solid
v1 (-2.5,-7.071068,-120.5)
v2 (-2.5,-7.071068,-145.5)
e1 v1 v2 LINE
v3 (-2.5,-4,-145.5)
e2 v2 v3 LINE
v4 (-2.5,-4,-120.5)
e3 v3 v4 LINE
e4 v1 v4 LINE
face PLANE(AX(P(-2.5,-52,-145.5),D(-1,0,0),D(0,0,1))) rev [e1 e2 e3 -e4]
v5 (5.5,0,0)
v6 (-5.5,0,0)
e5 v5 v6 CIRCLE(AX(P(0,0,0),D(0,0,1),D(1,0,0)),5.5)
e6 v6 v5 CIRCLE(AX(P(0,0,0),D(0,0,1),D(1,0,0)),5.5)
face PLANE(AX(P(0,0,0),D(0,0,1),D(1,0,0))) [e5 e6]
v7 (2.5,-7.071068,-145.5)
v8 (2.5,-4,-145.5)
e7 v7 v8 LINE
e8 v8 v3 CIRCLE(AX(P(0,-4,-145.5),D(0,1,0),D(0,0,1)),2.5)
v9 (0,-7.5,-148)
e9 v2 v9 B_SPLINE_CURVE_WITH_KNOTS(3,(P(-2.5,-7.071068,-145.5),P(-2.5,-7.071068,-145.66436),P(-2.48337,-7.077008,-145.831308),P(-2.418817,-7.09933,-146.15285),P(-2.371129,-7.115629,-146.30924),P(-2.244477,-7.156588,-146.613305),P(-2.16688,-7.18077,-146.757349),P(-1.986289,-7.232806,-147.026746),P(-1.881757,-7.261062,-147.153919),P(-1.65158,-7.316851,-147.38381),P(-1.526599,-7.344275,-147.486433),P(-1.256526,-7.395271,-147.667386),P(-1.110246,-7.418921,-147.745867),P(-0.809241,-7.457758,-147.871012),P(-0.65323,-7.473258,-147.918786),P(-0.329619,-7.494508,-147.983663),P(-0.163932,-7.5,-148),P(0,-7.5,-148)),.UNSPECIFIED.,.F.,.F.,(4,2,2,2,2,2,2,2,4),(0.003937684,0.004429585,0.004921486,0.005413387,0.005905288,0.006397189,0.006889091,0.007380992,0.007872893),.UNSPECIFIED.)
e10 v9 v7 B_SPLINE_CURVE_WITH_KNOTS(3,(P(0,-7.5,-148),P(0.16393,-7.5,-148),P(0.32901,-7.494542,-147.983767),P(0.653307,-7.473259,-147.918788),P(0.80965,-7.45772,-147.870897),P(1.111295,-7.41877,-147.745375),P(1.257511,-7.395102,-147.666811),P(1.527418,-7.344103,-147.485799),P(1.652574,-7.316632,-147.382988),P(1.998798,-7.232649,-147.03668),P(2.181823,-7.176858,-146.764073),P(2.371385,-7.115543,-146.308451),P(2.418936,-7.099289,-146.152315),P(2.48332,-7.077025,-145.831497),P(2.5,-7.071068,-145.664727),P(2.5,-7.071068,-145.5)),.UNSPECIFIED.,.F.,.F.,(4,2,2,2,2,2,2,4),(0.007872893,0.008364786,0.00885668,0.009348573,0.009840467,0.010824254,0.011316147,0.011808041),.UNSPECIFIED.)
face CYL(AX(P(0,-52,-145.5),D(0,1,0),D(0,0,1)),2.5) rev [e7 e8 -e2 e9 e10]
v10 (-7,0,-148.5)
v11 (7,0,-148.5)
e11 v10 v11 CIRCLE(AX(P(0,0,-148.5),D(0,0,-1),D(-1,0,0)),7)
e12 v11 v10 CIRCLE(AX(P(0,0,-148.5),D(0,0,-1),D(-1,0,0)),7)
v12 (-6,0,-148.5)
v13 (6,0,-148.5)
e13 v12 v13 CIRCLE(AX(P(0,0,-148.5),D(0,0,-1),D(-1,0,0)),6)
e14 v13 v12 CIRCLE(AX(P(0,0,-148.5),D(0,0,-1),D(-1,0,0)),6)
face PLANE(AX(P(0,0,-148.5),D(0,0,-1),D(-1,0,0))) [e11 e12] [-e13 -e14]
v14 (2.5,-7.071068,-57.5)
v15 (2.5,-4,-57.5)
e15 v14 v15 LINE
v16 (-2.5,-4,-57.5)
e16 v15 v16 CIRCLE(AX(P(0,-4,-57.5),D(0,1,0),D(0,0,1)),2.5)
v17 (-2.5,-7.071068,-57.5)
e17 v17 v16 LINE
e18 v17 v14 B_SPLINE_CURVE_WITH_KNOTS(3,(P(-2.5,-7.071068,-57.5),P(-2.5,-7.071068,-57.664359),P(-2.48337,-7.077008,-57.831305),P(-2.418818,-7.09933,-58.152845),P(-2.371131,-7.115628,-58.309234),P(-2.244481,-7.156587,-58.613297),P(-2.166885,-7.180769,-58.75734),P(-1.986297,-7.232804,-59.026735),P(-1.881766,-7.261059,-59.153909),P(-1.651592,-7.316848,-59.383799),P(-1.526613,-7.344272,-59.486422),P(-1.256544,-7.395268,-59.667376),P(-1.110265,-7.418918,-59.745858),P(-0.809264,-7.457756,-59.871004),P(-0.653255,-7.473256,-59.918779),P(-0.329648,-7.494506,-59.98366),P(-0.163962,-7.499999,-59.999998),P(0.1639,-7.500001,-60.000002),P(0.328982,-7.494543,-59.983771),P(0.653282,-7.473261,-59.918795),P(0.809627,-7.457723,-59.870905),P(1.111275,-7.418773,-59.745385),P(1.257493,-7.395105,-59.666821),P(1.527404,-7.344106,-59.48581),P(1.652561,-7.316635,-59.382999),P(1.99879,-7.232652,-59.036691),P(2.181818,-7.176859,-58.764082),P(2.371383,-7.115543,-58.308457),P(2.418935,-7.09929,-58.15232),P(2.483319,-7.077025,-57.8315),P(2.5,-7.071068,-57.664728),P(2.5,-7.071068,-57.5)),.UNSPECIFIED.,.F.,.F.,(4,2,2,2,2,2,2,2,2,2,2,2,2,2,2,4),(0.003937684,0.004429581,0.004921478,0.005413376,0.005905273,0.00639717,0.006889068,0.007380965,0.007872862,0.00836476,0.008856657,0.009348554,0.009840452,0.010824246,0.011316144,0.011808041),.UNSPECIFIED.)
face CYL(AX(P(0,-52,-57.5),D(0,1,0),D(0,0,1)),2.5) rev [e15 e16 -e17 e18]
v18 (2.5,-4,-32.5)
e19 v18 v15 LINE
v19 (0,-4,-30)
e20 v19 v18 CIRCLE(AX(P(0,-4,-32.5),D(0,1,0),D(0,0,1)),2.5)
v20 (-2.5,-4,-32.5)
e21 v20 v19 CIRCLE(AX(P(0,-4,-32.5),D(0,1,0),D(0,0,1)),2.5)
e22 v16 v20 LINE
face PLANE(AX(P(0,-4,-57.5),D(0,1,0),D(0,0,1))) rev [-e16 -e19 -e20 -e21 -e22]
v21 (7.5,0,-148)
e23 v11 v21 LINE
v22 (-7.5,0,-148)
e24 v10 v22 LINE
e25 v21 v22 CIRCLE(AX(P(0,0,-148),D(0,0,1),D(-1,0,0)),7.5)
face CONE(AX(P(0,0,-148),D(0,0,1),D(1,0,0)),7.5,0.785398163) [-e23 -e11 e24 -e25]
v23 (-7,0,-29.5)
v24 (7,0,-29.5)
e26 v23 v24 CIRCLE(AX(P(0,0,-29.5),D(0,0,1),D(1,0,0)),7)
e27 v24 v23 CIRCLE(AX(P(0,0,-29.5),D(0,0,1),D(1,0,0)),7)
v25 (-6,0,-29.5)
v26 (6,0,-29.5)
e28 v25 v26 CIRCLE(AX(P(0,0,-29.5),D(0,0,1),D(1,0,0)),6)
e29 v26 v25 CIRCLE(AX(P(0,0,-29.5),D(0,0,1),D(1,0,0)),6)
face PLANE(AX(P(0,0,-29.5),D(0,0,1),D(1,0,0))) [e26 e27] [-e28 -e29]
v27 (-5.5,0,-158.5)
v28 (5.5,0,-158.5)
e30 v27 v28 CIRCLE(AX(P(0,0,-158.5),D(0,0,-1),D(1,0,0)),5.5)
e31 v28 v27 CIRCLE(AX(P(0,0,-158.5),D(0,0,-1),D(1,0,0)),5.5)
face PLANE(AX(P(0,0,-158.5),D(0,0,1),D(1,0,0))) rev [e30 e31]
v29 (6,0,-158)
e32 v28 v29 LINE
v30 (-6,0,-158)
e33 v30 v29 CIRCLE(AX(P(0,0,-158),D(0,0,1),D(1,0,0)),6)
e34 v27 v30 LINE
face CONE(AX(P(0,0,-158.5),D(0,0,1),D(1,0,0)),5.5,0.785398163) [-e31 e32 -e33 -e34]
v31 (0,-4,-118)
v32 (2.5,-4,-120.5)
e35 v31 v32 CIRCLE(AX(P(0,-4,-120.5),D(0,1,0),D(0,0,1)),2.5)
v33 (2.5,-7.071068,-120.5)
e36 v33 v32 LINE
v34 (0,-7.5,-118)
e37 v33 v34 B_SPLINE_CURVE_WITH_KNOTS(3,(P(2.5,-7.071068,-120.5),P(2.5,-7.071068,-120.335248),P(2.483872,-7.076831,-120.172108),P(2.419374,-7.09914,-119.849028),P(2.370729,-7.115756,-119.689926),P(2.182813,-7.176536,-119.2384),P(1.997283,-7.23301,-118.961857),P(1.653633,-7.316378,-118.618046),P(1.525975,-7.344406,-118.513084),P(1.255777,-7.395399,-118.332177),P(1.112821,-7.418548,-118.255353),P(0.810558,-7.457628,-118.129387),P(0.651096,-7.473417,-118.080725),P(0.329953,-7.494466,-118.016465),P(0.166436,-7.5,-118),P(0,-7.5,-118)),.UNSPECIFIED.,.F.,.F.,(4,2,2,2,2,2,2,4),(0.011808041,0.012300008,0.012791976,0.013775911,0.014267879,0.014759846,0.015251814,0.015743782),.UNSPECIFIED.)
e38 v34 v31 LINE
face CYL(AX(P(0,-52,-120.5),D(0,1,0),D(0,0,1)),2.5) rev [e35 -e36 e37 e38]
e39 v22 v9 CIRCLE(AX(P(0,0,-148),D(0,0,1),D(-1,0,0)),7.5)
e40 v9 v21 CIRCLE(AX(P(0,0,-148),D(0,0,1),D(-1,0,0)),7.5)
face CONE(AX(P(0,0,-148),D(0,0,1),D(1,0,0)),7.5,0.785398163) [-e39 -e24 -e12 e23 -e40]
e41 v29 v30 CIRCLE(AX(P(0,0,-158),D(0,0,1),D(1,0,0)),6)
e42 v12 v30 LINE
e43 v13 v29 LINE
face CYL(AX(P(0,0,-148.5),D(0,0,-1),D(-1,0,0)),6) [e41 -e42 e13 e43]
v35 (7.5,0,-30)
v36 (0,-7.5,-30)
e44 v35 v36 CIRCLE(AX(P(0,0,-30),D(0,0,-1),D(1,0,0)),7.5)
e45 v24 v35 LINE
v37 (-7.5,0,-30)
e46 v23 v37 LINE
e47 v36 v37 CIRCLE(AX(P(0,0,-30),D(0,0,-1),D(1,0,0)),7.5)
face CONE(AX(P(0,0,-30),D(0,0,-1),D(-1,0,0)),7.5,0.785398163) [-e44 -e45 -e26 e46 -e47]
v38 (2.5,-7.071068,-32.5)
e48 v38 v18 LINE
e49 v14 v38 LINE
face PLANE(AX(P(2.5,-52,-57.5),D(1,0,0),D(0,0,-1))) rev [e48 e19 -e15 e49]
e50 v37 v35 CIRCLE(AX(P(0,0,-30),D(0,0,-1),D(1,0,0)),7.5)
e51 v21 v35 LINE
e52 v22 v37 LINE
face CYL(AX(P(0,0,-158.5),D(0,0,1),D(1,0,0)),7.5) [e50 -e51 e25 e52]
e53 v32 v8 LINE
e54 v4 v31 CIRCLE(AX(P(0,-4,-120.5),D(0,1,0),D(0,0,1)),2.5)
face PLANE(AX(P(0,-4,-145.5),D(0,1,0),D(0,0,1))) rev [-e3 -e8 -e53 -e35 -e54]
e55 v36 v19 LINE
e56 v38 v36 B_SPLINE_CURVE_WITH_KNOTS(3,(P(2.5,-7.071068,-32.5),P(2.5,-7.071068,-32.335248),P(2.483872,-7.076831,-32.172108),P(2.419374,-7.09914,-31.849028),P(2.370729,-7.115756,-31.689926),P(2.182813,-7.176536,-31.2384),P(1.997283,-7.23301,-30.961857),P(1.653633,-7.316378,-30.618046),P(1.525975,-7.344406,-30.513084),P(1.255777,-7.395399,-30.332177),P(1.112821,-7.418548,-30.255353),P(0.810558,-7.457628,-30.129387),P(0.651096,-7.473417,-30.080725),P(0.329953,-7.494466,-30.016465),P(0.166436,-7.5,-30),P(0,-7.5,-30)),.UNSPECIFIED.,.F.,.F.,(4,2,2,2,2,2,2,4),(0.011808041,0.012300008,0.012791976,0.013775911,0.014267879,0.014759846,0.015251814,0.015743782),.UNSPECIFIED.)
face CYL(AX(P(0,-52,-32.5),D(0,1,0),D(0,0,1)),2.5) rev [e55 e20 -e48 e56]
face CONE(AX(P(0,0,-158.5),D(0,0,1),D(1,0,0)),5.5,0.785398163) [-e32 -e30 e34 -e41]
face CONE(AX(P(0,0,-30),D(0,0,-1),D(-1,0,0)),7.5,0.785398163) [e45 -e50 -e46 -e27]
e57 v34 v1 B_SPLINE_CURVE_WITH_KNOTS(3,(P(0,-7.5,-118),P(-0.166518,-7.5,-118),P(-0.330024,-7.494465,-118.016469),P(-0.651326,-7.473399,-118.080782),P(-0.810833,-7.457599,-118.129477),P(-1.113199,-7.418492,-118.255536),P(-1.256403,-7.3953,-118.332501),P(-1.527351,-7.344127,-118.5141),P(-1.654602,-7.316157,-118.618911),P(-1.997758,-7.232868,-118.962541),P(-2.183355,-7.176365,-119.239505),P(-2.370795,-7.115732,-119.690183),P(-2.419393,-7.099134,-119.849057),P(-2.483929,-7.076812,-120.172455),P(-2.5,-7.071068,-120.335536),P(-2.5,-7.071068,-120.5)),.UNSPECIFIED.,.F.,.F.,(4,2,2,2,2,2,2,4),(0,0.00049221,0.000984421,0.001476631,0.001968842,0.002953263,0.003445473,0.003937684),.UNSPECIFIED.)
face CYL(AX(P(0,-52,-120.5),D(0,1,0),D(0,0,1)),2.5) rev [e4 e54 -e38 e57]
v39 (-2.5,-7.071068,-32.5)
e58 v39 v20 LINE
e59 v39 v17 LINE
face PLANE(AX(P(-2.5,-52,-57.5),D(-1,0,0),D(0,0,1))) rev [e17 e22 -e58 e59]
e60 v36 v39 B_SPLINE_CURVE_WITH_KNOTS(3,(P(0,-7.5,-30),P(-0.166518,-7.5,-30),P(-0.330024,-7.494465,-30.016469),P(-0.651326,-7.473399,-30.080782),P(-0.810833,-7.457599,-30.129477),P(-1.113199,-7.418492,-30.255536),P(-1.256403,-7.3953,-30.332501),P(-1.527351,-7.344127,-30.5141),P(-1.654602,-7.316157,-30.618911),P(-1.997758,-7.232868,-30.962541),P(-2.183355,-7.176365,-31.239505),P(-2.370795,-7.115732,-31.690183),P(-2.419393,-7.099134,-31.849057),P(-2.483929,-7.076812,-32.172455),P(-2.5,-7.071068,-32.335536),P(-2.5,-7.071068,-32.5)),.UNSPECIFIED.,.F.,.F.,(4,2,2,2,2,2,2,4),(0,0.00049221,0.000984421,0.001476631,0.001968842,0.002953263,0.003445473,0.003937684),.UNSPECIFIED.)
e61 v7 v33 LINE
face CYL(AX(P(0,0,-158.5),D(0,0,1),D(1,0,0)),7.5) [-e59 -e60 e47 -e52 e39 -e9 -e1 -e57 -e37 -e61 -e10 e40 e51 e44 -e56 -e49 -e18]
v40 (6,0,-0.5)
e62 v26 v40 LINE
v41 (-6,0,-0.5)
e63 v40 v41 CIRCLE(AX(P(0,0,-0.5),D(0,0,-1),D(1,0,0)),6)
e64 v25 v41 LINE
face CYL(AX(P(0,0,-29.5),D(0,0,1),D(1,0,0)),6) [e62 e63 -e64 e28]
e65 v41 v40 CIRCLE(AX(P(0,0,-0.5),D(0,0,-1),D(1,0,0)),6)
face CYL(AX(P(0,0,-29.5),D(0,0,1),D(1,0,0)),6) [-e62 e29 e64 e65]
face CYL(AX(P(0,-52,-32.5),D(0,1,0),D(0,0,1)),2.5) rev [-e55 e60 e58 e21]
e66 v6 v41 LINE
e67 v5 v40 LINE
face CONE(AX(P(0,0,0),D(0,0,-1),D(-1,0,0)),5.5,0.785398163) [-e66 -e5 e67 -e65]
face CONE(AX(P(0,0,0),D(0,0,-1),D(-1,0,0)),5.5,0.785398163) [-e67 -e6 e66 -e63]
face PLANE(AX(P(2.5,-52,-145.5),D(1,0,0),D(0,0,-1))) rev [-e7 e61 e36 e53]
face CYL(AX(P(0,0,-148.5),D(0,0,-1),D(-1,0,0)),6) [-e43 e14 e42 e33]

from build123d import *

# Parameters (mm, degrees)
SKETCH_1_R          = 7.5
EXTRUDE_1_DEPTH     = 158.5
SKETCH_5_OUTSIDE_W  = 48.982
SKETCH_5_OUTSIDE_H  = 48.982
SKETCH_5_OUTSIDE_R  = 6
CUT_EXTRUDE_3_DEPTH = 29.5
CHAMFER_2_SIZE      = 0.5
SKETCH_2_OUTSIDE_W  = 48.982
SKETCH_2_OUTSIDE_H  = 48.982
SKETCH_2_OUTSIDE_R  = 6
CUT_EXTRUDE_4_DEPTH = 10
CHAMFER_3_SIZE      = 0.5
CUT_EXTRUDE_START   = -4
CUT_EXTRUDE_5_DEPTH = 48


with BuildPart() as part:
    # 草图1 → 凸台-拉伸1 (new body)
    with BuildSketch(Plane.XY):
        Circle(SKETCH_1_R)
    extrude(amount=-EXTRUDE_1_DEPTH)

    # 草图5 outside → 切除-拉伸3 (cut)
    with BuildSketch(Plane.XY):
        Rectangle(SKETCH_5_OUTSIDE_W, SKETCH_5_OUTSIDE_H)
        Circle(SKETCH_5_OUTSIDE_R, mode=Mode.SUBTRACT)
    extrude(amount=-CUT_EXTRUDE_3_DEPTH, mode=Mode.SUBTRACT)

    # 倒角2
    chamfer_2_edges = [part.edges().sort_by_distance(p)[0] for p in [
        (-7.5, 0, -29.5),
        (-6, 0, 0),
    ]]
    chamfer(chamfer_2_edges, length=CHAMFER_2_SIZE)

    # 草图2 outside → 切除-拉伸4 (cut)
    with BuildSketch(Plane(origin=(0, 0, -158.5), x_dir=(-1, 0, 0), z_dir=(0, 0, -1))):
        Rectangle(SKETCH_2_OUTSIDE_W, SKETCH_2_OUTSIDE_H)
        with Locations(Location((0, 0, 0), (0, 0, 180))):
            Circle(SKETCH_2_OUTSIDE_R, mode=Mode.SUBTRACT)
    extrude(amount=-CUT_EXTRUDE_4_DEPTH, mode=Mode.SUBTRACT)

    # 倒角3
    chamfer_3_edges = [part.edges().sort_by_distance(p)[0] for p in [
        (-7.5, 0, -148.5),
        (-6, 0, -158.5),
    ]]
    chamfer(chamfer_3_edges, length=CHAMFER_3_SIZE)

    # 草图8 → 切除-拉伸5 (cut)
    with BuildSketch(Plane(origin=(0, 0, 0), x_dir=(1, 0, 0), z_dir=(0, 1, 0)).offset(CUT_EXTRUDE_START)):
        with BuildLine():
            Line((2.5, 57.5), (2.5, 32.5))
            ThreePointArc((2.5, 32.5), (0, 30), (-2.5, 32.5))
            Line((-2.5, 32.5), (-2.5, 57.5))
            ThreePointArc((-2.5, 57.5), (0, 60), (2.5, 57.5))
        make_face()
        with BuildLine():
            Line((2.5, 145.5), (2.5, 120.5))
            ThreePointArc((2.5, 120.5), (0, 118), (-2.5, 120.5))
            Line((-2.5, 120.5), (-2.5, 145.5))
            ThreePointArc((-2.5, 145.5), (0, 148), (2.5, 145.5))
        make_face()
    extrude(amount=-CUT_EXTRUDE_5_DEPTH, mode=Mode.SUBTRACT)


solid = part.part
